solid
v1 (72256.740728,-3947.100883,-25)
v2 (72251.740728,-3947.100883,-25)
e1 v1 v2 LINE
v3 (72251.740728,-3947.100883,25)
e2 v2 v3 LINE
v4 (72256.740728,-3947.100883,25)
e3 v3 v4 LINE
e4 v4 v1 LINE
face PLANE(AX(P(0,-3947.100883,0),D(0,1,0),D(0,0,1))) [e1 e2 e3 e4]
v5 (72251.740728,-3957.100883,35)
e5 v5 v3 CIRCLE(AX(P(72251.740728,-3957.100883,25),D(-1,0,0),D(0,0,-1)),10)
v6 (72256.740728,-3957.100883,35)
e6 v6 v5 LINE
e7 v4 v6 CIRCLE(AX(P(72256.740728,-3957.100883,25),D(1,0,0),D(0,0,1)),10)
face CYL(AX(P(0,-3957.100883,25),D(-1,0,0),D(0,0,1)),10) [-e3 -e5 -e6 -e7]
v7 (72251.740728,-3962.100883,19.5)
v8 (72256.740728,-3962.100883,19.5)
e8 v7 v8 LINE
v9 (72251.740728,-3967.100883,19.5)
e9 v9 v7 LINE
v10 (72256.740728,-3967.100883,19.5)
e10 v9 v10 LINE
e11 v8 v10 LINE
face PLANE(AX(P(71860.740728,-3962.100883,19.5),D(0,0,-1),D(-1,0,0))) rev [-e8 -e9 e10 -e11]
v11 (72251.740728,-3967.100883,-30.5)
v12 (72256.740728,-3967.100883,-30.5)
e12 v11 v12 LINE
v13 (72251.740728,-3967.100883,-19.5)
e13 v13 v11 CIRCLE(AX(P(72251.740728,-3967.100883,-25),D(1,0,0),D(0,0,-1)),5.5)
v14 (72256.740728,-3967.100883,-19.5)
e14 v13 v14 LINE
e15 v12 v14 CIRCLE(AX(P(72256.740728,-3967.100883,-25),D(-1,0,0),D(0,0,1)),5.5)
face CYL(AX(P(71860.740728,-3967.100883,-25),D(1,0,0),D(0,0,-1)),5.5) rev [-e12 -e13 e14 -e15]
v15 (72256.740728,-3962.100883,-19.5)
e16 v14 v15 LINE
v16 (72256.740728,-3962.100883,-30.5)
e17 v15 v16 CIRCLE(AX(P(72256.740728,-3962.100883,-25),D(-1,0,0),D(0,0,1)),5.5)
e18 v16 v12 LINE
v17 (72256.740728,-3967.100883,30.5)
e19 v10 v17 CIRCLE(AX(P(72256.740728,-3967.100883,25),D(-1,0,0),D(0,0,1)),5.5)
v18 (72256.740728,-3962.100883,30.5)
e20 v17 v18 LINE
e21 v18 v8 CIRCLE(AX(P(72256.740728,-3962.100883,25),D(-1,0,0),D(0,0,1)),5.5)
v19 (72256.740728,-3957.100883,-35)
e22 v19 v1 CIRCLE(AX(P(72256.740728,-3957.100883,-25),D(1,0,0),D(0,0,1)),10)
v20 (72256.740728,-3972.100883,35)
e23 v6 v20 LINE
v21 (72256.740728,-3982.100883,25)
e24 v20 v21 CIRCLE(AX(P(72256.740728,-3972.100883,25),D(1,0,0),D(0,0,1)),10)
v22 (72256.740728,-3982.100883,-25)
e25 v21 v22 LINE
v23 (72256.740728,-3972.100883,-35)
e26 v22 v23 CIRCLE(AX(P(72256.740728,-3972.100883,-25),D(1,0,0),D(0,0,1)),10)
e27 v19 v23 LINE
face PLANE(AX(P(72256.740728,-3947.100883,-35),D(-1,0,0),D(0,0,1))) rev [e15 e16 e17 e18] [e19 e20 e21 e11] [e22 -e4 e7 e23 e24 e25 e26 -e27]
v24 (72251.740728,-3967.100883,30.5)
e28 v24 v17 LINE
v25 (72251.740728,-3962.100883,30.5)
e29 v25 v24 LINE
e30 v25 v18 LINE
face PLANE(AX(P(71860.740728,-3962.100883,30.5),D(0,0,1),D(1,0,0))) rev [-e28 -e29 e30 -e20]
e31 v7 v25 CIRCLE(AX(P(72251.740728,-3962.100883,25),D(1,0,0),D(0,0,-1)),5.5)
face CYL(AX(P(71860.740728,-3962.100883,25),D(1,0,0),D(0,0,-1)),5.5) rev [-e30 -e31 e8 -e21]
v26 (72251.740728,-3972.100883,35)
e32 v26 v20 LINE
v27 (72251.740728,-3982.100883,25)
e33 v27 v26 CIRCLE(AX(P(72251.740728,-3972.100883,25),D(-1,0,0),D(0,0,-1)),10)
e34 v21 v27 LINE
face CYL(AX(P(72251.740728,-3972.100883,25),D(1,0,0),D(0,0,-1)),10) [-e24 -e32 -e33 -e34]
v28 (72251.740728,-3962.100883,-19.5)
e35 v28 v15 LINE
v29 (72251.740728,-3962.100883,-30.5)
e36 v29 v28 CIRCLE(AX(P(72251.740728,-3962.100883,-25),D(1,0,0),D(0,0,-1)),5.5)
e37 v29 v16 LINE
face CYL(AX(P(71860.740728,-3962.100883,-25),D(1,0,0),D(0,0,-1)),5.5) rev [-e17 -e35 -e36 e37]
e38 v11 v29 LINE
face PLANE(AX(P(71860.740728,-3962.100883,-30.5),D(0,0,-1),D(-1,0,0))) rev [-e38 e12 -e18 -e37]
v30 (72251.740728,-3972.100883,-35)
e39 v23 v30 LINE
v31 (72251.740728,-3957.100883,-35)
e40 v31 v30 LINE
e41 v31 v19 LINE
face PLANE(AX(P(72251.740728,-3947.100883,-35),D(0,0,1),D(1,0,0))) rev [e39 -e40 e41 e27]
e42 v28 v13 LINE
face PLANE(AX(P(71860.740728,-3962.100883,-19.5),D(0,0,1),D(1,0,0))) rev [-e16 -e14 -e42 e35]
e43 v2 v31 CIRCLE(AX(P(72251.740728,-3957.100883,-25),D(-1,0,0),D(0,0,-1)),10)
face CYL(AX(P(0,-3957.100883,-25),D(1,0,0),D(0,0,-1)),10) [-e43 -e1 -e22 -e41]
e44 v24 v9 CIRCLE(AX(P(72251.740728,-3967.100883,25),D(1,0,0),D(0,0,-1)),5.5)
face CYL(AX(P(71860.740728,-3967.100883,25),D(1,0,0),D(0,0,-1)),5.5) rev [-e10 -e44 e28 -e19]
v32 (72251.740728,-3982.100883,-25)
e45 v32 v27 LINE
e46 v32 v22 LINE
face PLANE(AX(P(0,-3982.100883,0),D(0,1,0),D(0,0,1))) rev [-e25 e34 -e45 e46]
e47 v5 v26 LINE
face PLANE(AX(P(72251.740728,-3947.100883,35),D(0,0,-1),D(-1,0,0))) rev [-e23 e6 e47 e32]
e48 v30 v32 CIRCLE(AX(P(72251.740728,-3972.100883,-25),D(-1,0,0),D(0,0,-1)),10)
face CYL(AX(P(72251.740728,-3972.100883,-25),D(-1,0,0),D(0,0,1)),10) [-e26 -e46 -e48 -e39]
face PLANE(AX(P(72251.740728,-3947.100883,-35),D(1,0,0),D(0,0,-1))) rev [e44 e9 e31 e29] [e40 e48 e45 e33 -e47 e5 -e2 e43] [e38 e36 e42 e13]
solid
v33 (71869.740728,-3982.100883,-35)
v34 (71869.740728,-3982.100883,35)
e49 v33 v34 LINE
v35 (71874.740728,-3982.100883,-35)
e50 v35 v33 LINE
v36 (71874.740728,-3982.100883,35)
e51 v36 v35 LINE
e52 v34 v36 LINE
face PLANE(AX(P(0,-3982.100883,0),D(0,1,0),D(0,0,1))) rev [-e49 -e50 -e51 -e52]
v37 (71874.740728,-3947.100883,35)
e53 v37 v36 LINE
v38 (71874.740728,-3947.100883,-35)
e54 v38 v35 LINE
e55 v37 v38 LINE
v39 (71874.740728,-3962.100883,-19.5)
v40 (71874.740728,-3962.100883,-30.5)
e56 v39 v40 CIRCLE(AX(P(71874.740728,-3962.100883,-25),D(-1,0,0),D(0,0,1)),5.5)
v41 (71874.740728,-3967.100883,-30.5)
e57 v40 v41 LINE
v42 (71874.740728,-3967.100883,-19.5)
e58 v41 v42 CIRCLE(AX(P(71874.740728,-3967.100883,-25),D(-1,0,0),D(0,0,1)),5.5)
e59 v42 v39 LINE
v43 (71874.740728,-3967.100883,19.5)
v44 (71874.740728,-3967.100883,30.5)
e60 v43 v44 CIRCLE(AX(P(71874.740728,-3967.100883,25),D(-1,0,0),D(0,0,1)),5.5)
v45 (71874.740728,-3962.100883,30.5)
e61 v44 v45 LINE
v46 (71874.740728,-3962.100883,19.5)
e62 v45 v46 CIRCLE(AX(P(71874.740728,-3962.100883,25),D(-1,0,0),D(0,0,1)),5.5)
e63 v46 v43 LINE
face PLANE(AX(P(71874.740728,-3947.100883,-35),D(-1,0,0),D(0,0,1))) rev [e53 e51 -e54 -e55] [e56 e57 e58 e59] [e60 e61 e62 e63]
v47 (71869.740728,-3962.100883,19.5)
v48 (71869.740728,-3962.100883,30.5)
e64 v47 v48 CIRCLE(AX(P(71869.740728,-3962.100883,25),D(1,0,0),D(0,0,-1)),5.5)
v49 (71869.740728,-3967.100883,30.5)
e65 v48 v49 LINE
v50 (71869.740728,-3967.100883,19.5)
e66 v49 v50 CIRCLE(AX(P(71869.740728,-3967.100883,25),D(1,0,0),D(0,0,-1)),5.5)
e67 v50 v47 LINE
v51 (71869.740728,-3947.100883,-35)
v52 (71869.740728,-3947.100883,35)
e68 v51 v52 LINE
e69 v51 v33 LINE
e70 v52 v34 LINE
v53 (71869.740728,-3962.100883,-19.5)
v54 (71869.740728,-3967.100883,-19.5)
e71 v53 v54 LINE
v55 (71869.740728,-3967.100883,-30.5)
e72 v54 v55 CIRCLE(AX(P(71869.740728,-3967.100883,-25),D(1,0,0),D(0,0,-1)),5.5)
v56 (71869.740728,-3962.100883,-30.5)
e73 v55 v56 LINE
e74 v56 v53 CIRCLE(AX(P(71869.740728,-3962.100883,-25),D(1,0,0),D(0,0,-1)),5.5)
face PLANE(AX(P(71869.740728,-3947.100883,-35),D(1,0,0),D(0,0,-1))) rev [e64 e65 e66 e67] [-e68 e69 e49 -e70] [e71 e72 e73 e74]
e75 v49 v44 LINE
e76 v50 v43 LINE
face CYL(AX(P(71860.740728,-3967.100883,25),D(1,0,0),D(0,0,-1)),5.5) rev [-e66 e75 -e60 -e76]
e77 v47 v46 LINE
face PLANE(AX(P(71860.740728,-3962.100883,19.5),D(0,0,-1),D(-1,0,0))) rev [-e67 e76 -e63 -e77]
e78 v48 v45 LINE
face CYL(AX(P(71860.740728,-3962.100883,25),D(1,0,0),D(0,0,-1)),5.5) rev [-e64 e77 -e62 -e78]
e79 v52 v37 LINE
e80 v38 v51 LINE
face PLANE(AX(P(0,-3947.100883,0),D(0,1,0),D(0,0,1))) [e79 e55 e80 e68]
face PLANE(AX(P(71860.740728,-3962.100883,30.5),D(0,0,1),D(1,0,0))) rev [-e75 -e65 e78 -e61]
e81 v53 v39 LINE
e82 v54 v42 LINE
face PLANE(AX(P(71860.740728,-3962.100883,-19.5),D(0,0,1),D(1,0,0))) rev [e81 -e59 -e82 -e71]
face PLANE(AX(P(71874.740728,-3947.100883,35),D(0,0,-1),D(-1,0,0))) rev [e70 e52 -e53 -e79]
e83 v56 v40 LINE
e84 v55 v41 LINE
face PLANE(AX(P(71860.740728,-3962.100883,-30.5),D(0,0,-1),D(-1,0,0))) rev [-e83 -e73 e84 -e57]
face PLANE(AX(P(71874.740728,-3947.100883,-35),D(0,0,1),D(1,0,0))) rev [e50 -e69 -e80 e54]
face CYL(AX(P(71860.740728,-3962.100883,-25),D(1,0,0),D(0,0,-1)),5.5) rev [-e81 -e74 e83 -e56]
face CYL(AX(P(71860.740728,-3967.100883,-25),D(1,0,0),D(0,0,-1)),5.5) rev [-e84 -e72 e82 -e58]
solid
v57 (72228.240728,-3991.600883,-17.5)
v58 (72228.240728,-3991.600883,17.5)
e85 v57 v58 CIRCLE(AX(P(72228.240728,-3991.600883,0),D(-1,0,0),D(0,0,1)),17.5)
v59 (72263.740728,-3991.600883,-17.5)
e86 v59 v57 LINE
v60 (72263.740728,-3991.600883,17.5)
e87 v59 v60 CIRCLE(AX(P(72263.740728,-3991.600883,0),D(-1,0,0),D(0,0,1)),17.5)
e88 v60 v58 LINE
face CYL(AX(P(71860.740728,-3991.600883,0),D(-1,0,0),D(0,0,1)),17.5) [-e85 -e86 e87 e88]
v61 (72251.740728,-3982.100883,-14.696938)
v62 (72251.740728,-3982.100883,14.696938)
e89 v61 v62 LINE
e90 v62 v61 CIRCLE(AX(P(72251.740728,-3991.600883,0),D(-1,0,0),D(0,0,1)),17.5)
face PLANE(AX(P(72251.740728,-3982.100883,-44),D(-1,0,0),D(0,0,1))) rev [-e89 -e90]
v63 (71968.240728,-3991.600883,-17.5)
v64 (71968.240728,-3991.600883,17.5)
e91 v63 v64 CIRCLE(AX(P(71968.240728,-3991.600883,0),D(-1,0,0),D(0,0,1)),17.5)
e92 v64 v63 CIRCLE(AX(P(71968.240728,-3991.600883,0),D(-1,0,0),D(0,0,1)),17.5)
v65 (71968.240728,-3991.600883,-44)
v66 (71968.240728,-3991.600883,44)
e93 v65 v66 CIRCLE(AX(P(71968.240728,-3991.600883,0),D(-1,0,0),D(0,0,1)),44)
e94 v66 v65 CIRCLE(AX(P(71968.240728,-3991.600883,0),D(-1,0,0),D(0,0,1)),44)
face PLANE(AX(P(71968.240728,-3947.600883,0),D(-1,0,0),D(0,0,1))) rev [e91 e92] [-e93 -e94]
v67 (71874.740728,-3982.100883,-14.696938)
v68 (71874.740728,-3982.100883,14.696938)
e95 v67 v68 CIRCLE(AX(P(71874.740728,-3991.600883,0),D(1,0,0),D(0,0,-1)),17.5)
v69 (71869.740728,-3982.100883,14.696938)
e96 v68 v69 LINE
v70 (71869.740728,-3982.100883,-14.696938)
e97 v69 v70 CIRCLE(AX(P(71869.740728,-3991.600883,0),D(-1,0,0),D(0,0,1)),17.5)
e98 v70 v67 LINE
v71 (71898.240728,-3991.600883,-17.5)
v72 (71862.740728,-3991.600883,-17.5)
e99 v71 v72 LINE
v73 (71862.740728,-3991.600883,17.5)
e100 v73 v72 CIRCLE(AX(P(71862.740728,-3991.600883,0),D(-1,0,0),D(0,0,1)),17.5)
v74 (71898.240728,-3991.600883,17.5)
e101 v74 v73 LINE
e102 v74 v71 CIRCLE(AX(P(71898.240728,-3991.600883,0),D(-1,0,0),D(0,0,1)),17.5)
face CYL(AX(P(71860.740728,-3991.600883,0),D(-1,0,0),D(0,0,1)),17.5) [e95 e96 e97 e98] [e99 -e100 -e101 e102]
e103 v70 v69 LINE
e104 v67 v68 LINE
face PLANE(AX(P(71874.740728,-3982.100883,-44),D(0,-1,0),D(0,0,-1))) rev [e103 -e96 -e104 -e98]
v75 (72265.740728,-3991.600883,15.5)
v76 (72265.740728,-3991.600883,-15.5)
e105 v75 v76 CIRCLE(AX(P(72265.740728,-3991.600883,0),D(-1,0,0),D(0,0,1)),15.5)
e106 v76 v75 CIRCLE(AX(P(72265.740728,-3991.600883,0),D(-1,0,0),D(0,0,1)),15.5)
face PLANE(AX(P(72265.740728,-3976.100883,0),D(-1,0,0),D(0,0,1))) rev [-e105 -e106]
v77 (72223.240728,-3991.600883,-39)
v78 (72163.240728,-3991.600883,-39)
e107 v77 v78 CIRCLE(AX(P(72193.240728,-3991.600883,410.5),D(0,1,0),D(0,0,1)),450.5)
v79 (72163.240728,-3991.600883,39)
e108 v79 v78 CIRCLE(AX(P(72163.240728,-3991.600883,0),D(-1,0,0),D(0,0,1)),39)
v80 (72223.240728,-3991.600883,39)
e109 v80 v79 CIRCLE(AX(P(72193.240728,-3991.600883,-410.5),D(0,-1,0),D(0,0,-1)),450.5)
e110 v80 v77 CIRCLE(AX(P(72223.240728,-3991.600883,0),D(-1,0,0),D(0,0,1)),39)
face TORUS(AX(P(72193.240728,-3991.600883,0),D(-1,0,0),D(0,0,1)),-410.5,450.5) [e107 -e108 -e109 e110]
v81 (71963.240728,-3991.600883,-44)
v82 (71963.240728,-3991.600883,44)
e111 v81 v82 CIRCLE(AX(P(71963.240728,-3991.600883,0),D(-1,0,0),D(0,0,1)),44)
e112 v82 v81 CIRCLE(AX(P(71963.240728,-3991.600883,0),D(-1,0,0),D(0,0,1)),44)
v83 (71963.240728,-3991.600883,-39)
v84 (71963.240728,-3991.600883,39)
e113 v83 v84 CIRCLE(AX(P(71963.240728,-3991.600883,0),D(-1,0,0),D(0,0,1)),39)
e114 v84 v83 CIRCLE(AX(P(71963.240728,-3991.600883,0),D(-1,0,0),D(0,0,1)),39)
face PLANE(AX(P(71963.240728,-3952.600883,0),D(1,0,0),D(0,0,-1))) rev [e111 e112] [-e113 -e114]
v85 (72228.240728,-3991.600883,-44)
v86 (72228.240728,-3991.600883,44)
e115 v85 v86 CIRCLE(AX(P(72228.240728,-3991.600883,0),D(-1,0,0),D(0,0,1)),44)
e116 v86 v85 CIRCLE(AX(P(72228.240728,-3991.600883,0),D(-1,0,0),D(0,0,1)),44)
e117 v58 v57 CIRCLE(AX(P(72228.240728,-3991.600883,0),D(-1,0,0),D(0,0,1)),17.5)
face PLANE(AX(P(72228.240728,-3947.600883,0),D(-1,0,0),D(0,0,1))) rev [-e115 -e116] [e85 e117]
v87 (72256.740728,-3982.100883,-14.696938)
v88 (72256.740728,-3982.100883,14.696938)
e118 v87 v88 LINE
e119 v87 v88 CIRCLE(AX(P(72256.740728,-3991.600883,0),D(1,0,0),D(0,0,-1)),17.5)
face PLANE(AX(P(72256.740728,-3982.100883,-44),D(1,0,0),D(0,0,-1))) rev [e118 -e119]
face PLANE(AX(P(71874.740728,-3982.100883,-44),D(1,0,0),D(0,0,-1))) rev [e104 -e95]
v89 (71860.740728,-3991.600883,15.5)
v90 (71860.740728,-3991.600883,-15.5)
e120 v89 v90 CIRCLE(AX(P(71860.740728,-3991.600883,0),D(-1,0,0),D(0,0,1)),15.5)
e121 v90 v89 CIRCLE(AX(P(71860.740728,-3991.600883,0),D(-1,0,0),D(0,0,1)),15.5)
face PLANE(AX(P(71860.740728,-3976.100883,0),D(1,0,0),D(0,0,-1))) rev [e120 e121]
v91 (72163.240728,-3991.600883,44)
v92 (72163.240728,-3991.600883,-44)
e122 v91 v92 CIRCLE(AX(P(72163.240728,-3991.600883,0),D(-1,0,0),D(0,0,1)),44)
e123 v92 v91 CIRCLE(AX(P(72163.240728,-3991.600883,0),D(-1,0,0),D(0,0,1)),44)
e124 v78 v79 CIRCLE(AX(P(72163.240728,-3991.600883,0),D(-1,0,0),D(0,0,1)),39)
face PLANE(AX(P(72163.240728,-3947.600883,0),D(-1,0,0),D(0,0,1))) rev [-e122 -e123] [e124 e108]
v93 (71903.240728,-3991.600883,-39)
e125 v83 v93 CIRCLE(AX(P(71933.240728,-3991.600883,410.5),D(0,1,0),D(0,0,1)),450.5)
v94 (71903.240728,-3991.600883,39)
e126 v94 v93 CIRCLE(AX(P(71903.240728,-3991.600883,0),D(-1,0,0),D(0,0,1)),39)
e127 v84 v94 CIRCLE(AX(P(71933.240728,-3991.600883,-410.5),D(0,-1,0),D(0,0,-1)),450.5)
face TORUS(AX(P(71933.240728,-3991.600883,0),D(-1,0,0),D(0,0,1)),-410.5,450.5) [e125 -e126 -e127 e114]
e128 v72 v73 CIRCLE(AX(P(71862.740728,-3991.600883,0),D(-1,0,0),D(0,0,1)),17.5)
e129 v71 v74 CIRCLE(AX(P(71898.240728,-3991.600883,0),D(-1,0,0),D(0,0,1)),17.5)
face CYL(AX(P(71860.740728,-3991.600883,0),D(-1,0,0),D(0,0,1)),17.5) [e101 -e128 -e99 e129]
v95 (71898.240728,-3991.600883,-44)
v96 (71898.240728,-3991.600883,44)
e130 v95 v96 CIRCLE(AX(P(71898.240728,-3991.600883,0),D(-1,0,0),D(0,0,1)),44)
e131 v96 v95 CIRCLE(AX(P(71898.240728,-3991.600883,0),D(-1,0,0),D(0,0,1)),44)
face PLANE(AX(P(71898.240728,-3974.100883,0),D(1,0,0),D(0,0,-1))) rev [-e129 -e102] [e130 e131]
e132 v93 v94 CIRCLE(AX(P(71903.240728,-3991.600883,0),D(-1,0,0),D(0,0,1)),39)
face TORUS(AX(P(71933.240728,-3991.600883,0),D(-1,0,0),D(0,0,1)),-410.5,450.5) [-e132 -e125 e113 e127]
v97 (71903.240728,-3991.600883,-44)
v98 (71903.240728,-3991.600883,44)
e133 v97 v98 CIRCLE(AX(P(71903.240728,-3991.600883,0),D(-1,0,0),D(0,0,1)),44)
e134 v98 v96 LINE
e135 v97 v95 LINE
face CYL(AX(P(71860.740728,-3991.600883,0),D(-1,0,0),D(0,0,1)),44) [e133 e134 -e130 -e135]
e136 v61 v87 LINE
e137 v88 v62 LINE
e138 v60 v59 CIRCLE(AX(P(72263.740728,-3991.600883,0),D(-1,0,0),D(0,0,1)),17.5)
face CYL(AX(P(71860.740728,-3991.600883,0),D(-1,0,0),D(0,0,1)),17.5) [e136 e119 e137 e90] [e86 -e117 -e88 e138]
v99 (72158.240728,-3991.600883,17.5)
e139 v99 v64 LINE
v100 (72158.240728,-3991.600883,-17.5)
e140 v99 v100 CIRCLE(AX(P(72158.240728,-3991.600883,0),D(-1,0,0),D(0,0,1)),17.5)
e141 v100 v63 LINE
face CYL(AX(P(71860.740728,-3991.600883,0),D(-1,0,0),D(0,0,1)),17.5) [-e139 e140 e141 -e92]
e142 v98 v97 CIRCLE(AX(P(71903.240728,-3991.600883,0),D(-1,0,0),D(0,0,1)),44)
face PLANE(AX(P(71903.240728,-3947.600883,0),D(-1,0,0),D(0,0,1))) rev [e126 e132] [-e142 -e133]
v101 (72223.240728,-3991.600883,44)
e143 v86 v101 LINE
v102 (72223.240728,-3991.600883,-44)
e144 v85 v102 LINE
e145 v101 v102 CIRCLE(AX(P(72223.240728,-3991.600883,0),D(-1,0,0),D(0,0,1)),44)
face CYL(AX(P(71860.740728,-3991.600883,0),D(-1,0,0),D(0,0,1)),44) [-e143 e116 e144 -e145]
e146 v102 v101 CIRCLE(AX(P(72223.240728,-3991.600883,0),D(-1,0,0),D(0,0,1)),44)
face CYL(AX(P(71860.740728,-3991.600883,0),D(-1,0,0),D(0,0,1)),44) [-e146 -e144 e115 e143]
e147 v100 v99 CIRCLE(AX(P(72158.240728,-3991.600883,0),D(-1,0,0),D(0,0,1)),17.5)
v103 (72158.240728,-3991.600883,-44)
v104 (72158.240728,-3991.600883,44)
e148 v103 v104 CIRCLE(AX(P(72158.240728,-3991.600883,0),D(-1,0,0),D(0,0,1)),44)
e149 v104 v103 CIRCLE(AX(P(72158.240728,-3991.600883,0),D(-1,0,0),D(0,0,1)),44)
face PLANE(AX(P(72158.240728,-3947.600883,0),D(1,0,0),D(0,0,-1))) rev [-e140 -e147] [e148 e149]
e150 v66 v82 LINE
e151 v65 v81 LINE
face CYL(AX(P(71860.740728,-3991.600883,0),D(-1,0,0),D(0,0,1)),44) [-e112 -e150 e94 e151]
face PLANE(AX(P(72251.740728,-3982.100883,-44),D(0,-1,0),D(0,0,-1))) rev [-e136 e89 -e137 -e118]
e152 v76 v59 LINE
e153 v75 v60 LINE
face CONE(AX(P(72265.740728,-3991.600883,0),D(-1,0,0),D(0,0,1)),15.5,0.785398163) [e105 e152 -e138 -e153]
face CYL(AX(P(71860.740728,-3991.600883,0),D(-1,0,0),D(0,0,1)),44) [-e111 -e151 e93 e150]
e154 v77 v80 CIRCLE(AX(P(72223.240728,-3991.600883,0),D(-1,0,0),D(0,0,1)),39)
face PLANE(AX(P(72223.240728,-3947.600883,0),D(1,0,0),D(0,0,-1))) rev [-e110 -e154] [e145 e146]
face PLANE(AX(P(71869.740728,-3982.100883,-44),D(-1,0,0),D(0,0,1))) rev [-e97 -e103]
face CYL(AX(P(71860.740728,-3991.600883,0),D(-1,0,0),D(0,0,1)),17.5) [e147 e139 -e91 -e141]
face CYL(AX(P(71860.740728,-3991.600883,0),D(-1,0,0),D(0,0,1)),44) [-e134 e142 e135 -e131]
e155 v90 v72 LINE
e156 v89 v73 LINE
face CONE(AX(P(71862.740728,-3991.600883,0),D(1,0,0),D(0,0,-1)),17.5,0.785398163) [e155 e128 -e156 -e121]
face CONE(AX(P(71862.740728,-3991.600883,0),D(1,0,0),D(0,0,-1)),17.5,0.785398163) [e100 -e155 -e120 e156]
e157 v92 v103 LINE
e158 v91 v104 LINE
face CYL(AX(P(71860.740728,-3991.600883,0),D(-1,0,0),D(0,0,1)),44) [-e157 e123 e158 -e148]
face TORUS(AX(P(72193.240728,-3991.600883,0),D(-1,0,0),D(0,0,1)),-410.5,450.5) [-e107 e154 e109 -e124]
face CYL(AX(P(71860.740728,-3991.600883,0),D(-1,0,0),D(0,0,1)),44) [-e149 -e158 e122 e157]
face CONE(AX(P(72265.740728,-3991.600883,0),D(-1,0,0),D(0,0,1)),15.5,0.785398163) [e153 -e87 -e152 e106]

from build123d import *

# Parameters (mm, degrees)
CUT_EXTRUDE_1_DEPTH      = 72379.34823682
CUT_EXTRUDE_1_DEPTH_BACK = 72379.34823682
SKETCH_2_W               = 5
SKETCH_2_H               = 25.766795942
SKETCH_3_W               = 5
SKETCH_3_H               = 70
EXTRUDE_1_DEPTH          = 35
EXTRUDE_1_2_DEPTH        = 35
FILLET_1_R               = 10
CUT_EXTRUDE_2_DEPTH      = 4056.222125419
CUT_EXTRUDE_2_DEPTH_BACK = 4056.222125419


with BuildPart() as part:
    # 草图1 → 旋转1 (revolve)
    with BuildSketch(Plane.XY, mode=Mode.PRIVATE) as revolve_1_sk:
        with BuildLine():
            Line((72263.740728259, -3974.100882952), (72228.240728259, -3974.100882952))
            Line((72228.240728259, -3974.100882952), (72228.240728259, -3947.600882952))
            Line((72228.240728259, -3947.600882952), (72223.240728259, -3947.600882952))
            Line((72223.240728259, -3947.600882952), (72223.240728258, -3952.600882952))
            ThreePointArc((72223.240728258, -3952.600882952), (72193.240728259, -3951.600882952), (72163.240728259, -3952.600882952))
            Line((72163.240728259, -3952.600882952), (72163.240728259, -3947.600882952))
            Line((72163.240728259, -3947.600882952), (72158.240728259, -3947.600882952))
            Line((72158.240728259, -3947.600882952), (72158.240728259, -3974.100882952))
            Line((72158.240728259, -3974.100882952), (71968.240728259, -3974.100882952))
            Line((71968.240728259, -3974.100882952), (71968.240728259, -3947.600882952))
            Line((71968.240728259, -3947.600882952), (71963.240728259, -3947.600882952))
            Line((71963.240728259, -3947.600882952), (71963.240728258, -3952.600882952))
            ThreePointArc((71963.240728258, -3952.600882952), (71933.240728259, -3951.600882952), (71903.240728259, -3952.600882952))
            Line((71903.240728259, -3952.600882952), (71903.240728259, -3947.600882952))
            Line((71903.240728259, -3947.600882952), (71898.240728259, -3947.600882952))
            Line((71898.240728259, -3947.600882952), (71898.240728259, -3974.100882952))
            Line((71898.240728259, -3974.100882952), (71862.740728259, -3974.100882952))
            Line((71862.740728259, -3974.100882952), (71860.740728259, -3976.100882952))
            Line((71860.740728259, -3976.100882952), (71860.740728259, -3991.600882952))
            Line((71860.740728259, -3991.600882952), (72265.740728259, -3991.600882952))
            Line((72265.740728259, -3991.600882952), (72265.740728259, -3976.100882952))
            Line((72265.740728259, -3976.100882952), (72263.740728259, -3974.100882952))
        make_face()
    revolve(revolve_1_sk.sketch.rotate(Axis((71860.740728259, -3991.600882952, 0), (1, 0, 0)), 90), axis=Axis((71860.740728259, -3991.600882952, 0), (1, 0, 0)))

    # 草图2 → 切除-拉伸1 (cut, two sides: drawn at the far end of the back side and taken through both)
    with BuildSketch(Plane.XY.offset(-CUT_EXTRUDE_1_DEPTH_BACK)):
        with Locations((72254.240728259, -3969.217484981)):
            Rectangle(SKETCH_2_W, SKETCH_2_H)
        with Locations((71872.240728259, -3969.217484981)):
            Rectangle(SKETCH_2_W, SKETCH_2_H)
    extrude(amount=CUT_EXTRUDE_1_DEPTH + CUT_EXTRUDE_1_DEPTH_BACK, mode=Mode.SUBTRACT)


with BuildPart() as body_2:
    # 草图3 → 凸台-拉伸1 (new body)
    with BuildSketch(Plane(origin=(0, -3982.100882952, 0), x_dir=(1, 0, 0), z_dir=(0, 1, 0))):
        with Locations((72254.240728259, 0)):
            Rectangle(SKETCH_3_W, SKETCH_3_H)
    extrude(amount=EXTRUDE_1_DEPTH)

    # 圆角1
    fillet_1_edges = [body_2.edges().sort_by_distance(p)[0] for p in [
        (72254.240728259, -3947.100882952, -35),
        (72254.240728259, -3982.100882952, -35),
        (72254.240728259, -3982.100882952, 35),
        (72254.240728259, -3947.100882952, 35),
    ]]
    fillet(fillet_1_edges, radius=FILLET_1_R)


with BuildPart() as body_3:
    # 草图3 → Extrude 1 2 (new body)
    with BuildSketch(Plane(origin=(0, -3982.100882952, 0), x_dir=(1, 0, 0), z_dir=(0, 1, 0))):
        with Locations((71872.240728259, 0)):
            Rectangle(SKETCH_3_W, SKETCH_3_H)
    extrude(amount=EXTRUDE_1_2_DEPTH)


with BuildPart() as cut_extrude_2_tool:
    # 草图4 → 切除-拉伸2 (new, two sides: drawn at the far end of the back side and taken through both)
    with BuildSketch(Plane(origin=(72256.740728259, 0, 0), x_dir=(0, 0, -1), z_dir=(1, 0, 0)).offset(-CUT_EXTRUDE_2_DEPTH_BACK)):
        with BuildLine():
            Line((-19.5, -3962.100882952), (-19.5, -3967.100882952))
            ThreePointArc((-19.5, -3967.100882952), (-25, -3972.600882952), (-30.5, -3967.100882952))
            Line((-30.5, -3967.100882952), (-30.5, -3962.100882952))
            ThreePointArc((-30.5, -3962.100882952), (-25, -3956.600882952), (-19.5, -3962.100882952))
        make_face()
        with BuildLine():
            Line((19.5, -3962.100882952), (19.5, -3967.100882952))
            ThreePointArc((19.5, -3967.100882952), (25, -3972.600882952), (30.5, -3967.100882952))
            Line((30.5, -3967.100882952), (30.5, -3962.100882952))
            ThreePointArc((30.5, -3962.100882952), (25, -3956.600882952), (19.5, -3962.100882952))
        make_face()
    extrude(amount=CUT_EXTRUDE_2_DEPTH + CUT_EXTRUDE_2_DEPTH_BACK)


with BuildPart() as body_3_1:
    add(body_3.part)

    # 切除-拉伸2: cut by cut_extrude_2_tool
    add(cut_extrude_2_tool.part, mode=Mode.SUBTRACT)


with BuildPart() as body_2_1:
    add(body_2.part)

    # 切除-拉伸2: cut by cut_extrude_2_tool
    add(cut_extrude_2_tool.part, mode=Mode.SUBTRACT)


solid = Compound([part.part, body_3_1.part, body_2_1.part])
